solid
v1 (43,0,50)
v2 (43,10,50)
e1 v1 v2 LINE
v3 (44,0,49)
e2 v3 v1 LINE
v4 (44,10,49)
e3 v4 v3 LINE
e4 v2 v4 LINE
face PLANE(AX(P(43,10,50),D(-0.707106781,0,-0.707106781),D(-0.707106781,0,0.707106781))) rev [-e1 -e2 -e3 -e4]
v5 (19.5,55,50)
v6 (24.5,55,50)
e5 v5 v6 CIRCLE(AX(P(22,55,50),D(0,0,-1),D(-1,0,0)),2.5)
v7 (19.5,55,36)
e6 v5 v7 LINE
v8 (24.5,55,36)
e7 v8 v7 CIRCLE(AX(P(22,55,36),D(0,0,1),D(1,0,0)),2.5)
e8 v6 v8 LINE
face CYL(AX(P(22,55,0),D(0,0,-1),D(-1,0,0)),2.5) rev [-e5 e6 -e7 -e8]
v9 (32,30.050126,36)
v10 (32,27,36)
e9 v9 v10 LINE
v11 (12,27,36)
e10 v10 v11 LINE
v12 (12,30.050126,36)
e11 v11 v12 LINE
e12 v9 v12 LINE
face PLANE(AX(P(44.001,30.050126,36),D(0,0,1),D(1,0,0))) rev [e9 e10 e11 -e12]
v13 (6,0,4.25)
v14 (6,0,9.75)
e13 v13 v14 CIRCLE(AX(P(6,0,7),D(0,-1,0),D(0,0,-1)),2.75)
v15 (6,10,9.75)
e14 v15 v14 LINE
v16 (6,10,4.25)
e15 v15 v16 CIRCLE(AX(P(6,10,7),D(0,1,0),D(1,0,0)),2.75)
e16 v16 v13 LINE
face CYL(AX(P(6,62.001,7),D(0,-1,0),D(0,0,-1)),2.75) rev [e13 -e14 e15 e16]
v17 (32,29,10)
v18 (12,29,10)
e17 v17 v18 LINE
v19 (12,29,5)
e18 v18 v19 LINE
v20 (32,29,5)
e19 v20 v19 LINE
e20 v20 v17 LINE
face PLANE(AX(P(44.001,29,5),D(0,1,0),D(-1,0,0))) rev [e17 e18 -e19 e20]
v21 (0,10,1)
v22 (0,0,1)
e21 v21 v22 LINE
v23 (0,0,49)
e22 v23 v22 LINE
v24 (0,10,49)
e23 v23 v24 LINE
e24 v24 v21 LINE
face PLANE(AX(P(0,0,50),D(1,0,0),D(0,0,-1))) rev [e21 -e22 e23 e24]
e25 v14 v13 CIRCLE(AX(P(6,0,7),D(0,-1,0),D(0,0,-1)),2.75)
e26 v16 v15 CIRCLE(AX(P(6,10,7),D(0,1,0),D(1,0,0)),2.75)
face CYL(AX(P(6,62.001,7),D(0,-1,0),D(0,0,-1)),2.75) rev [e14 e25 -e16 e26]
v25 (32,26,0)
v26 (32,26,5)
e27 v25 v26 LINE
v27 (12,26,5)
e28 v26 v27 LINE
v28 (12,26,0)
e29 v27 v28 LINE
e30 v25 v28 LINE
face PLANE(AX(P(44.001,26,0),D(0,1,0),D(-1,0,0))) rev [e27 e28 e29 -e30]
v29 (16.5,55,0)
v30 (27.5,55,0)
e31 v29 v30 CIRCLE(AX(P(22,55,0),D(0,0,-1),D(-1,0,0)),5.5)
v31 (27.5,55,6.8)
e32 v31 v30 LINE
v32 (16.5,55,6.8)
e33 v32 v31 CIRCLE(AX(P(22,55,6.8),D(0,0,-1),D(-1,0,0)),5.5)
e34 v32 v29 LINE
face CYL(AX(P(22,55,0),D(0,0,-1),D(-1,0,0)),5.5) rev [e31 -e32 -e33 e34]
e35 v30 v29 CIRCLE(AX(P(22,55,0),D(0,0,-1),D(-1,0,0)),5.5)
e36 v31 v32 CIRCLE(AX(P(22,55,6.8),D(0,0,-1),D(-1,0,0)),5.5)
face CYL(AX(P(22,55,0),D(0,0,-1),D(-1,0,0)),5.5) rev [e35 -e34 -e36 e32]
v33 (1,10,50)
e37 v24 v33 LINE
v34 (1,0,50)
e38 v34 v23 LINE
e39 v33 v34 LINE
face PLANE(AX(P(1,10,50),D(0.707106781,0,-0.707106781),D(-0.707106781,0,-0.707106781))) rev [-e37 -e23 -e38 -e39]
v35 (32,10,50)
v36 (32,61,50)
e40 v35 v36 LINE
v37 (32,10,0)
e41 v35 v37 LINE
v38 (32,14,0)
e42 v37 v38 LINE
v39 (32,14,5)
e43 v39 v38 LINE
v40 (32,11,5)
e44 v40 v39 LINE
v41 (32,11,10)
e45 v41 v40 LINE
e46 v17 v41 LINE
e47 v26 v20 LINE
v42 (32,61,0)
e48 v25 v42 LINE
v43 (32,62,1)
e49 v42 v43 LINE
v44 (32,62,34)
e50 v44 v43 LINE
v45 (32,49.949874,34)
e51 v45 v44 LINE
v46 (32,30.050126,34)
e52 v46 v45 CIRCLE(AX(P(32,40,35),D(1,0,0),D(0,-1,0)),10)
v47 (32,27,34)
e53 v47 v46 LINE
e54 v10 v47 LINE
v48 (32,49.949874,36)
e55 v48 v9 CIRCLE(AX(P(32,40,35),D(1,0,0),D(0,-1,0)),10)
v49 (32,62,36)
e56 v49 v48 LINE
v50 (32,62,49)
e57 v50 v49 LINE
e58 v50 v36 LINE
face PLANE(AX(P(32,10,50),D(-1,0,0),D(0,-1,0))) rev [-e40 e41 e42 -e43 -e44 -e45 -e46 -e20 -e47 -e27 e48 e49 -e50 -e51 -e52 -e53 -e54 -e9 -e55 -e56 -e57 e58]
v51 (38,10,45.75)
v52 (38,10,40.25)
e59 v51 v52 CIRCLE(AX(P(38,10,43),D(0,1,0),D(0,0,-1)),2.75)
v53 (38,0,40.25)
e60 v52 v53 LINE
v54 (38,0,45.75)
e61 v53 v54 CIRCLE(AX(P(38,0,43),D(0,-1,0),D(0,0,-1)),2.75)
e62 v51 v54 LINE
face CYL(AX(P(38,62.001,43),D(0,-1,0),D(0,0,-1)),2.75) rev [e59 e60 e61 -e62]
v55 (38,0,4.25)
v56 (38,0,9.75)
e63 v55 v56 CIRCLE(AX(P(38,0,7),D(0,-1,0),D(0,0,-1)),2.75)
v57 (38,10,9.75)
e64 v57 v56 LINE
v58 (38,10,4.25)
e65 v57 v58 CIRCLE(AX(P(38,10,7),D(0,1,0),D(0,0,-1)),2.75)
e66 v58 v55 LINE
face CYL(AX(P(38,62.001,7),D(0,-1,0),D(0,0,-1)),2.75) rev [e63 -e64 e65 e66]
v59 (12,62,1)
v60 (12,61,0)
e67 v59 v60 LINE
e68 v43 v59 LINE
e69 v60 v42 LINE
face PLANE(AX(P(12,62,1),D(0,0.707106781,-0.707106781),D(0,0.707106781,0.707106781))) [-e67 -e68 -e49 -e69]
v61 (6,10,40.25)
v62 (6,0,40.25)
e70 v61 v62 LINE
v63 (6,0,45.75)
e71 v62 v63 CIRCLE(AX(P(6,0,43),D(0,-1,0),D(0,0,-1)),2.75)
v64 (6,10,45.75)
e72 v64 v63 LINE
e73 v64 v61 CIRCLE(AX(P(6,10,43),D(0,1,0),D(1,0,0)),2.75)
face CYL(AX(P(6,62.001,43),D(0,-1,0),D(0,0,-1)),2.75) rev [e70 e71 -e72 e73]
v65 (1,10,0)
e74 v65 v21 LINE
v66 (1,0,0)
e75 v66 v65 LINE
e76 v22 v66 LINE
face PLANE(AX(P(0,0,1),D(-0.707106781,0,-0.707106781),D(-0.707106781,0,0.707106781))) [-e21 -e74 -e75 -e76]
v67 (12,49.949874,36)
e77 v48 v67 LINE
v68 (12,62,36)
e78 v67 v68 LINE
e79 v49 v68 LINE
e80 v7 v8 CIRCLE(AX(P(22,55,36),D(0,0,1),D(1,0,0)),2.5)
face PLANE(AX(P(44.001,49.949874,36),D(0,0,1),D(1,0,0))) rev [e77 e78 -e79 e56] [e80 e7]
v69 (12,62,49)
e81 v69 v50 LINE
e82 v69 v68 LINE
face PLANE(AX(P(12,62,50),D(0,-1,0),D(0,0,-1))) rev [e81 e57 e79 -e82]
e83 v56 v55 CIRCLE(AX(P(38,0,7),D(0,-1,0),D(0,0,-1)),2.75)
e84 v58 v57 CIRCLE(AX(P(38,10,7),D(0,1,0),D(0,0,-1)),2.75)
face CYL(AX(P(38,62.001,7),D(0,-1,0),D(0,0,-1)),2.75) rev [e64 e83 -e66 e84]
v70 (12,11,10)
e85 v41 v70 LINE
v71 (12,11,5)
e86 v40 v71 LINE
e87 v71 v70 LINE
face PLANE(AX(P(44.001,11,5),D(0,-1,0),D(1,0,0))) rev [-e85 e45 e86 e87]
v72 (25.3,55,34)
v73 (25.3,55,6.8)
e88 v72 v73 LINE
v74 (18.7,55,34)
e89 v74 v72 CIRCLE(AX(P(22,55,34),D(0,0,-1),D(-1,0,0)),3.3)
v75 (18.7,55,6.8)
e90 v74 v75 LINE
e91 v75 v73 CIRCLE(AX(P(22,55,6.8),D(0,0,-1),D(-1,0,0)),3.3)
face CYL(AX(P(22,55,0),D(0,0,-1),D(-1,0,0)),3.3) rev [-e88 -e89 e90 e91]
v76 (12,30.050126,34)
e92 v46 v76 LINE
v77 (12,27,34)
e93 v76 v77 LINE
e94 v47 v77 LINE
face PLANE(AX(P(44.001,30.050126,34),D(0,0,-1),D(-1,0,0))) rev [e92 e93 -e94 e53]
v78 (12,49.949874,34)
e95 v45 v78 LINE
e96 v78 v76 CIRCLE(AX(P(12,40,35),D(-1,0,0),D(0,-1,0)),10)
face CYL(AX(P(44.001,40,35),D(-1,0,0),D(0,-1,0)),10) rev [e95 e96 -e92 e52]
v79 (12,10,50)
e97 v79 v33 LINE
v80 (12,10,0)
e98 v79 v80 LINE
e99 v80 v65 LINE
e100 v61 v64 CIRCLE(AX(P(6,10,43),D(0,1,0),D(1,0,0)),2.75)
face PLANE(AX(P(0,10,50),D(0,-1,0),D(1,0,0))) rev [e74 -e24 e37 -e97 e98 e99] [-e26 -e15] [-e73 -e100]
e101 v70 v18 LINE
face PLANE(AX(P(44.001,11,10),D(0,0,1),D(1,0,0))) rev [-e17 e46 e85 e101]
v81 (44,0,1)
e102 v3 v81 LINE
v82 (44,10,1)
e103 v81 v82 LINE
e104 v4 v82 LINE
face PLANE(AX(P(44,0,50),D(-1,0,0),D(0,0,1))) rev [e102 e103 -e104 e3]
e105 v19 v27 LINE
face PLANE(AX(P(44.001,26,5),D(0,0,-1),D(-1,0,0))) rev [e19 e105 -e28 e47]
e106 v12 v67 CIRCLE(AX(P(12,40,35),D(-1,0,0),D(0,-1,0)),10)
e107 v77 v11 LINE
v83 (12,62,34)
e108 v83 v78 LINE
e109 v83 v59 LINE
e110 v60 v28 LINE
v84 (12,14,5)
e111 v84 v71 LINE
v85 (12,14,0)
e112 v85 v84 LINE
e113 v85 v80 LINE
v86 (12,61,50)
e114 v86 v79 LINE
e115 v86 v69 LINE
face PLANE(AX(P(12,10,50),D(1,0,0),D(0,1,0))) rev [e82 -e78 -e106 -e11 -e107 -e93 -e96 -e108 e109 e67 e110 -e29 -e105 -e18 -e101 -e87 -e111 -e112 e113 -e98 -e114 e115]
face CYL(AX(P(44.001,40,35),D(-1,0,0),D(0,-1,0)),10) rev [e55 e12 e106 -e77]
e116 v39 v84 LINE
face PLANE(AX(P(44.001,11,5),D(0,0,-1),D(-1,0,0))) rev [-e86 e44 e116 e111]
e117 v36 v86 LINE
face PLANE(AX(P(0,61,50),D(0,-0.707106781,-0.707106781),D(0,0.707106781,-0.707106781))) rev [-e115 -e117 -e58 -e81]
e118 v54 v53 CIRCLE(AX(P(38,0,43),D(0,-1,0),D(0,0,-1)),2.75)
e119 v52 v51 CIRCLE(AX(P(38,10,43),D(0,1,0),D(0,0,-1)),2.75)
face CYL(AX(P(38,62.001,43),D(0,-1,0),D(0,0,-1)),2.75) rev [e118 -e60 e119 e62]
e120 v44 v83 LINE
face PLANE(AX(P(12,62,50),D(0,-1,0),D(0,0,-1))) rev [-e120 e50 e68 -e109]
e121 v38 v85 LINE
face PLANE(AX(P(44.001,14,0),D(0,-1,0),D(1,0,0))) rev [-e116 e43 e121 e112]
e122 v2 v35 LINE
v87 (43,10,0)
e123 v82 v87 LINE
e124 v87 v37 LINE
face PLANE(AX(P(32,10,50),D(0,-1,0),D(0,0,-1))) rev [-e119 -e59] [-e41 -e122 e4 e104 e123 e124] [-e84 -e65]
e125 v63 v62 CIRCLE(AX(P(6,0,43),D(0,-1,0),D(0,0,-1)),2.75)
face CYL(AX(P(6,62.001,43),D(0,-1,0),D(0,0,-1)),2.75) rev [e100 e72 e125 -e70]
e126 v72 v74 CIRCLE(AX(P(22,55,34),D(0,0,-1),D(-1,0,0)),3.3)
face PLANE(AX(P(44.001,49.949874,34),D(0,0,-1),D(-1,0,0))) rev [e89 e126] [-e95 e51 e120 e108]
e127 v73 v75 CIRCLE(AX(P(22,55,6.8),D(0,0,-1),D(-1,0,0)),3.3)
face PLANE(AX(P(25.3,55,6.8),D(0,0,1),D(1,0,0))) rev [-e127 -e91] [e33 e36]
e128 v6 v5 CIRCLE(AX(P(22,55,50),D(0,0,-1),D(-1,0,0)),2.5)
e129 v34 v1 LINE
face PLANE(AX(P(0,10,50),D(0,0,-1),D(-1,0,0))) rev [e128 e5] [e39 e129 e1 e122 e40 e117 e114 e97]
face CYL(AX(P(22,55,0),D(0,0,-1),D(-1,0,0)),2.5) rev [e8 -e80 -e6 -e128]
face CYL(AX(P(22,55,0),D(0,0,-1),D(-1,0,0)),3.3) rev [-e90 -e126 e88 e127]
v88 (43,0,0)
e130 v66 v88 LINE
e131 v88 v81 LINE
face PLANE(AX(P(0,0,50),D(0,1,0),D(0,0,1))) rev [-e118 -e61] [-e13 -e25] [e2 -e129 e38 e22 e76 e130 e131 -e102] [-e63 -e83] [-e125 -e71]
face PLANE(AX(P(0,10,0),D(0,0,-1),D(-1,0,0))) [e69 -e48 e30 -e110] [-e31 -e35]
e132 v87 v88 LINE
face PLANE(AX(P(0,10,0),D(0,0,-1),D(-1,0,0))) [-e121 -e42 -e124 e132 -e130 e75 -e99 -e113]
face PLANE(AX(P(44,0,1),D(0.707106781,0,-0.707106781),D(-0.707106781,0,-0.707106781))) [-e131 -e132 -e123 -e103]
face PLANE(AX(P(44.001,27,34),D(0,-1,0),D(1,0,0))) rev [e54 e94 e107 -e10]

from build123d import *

# Parameters (mm, degrees)
BOSS_EXTRUDE1_DEPTH                                  = 50
CUT_EXTRUDE1_REACH                                   = 92.995
SKETCH2_R                                            = 2.75
CUT_EXTRUDE2_REACH                                   = 87.837
HOLE_SIZE_PER_SOCKET_HEAD_CAP_SCREW_TYPE_D           = 6.6
HOLE_SIZE_PER_SOCKET_HEAD_CAP_SCREW_TYPE_DEPTH       = 34
HOLE_SIZE_PER_SOCKET_HEAD_CAP_SCREW_TYPE_CBORE_D     = 11
HOLE_SIZE_PER_SOCKET_HEAD_CAP_SCREW_TYPE_CBORE_DEPTH = 6.8
M6_TAPPED_HOLE1_D                                    = 5
CHAMFER1_SIZE                                        = 1


with BuildPart() as part:
    # Sketch1 → Boss-Extrude1 (new body)
    with BuildSketch(Plane.XY):
        Polygon((32, 10), (44, 10), (44, 0), (0, 0), (0, 10), (12, 10), (12, 62), (32, 62), align=None)
    extrude(amount=BOSS_EXTRUDE1_DEPTH)

    # Sketch2 → Cut-Extrude1 (cut, up to next)
    with BuildSketch(Plane.XZ, mode=Mode.PRIVATE) as cut_extrude1_sk1:
        with Locations(Location((6, 43, 0), (0, 0, 270))):
            Circle(SKETCH2_R)
    cut_extrude1_tool1 = extrude(cut_extrude1_sk1.sketch, amount=-CUT_EXTRUDE1_REACH, mode=Mode.PRIVATE) & part.part
    # Sketch2 → Cut-Extrude1 (cut, up to next)
    with BuildSketch(Plane.XZ, mode=Mode.PRIVATE) as cut_extrude1_sk2:
        with Locations(Location((6, 7, 0), (0, 0, 270))):
            Circle(SKETCH2_R)
    cut_extrude1_tool2 = extrude(cut_extrude1_sk2.sketch, amount=-CUT_EXTRUDE1_REACH, mode=Mode.PRIVATE) & part.part
    # Sketch2 → Cut-Extrude1 (cut, up to next)
    with BuildSketch(Plane.XZ, mode=Mode.PRIVATE) as cut_extrude1_sk3:
        with Locations(Location((38, 43, 0), (0, 0, 270))):
            Circle(SKETCH2_R)
    cut_extrude1_tool3 = extrude(cut_extrude1_sk3.sketch, amount=-CUT_EXTRUDE1_REACH, mode=Mode.PRIVATE) & part.part
    # Sketch2 → Cut-Extrude1 (cut, up to next)
    with BuildSketch(Plane.XZ, mode=Mode.PRIVATE) as cut_extrude1_sk4:
        with Locations(Location((38, 7, 0), (0, 0, 270))):
            Circle(SKETCH2_R)
    cut_extrude1_tool4 = extrude(cut_extrude1_sk4.sketch, amount=-CUT_EXTRUDE1_REACH, mode=Mode.PRIVATE) & part.part
    add(cut_extrude1_tool1.solids().sort_by_distance((6, 0, 43))[0], mode=Mode.SUBTRACT)
    add(cut_extrude1_tool2.solids().sort_by_distance((6, 0, 7))[0], mode=Mode.SUBTRACT)
    add(cut_extrude1_tool3.solids().sort_by_distance((38, 0, 43))[0], mode=Mode.SUBTRACT)
    add(cut_extrude1_tool4.solids().sort_by_distance((38, 0, 7))[0], mode=Mode.SUBTRACT)

    # Sketch3 → Cut-Extrude2 (cut, up to next)
    with BuildSketch(Plane.ZY.offset(-12), mode=Mode.PRIVATE) as cut_extrude2_sk1:
        with BuildLine():
            Line((34, 49.949874371), (34, 62))
            Line((34, 62), (36, 62))
            Line((36, 62), (36, 49.949874371))
            ThreePointArc((36, 49.949874371), (45, 40), (36, 30.050125629))
            Line((36, 30.050125629), (36, 27))
            Line((36, 27), (34, 27))
            Line((34, 27), (34, 30.050125629))
            ThreePointArc((34, 30.050125629), (25, 40), (34, 49.949874371))
        make_face()
    cut_extrude2_tool1 = extrude(cut_extrude2_sk1.sketch, amount=-CUT_EXTRUDE2_REACH, mode=Mode.PRIVATE) & part.part
    # Sketch3 → Cut-Extrude2 (cut, up to next)
    with BuildSketch(Plane.ZY.offset(-12), mode=Mode.PRIVATE) as cut_extrude2_sk2:
        Polygon((5, 26), (5, 29), (10, 29), (10, 11), (5, 11), (5, 14), (0, 14), (0, 26), align=None)
    cut_extrude2_tool2 = extrude(cut_extrude2_sk2.sketch, amount=-CUT_EXTRUDE2_REACH, mode=Mode.PRIVATE) & part.part
    add(cut_extrude2_tool1.solids().sort_by_distance((12, 40.915096, 35))[0], mode=Mode.SUBTRACT)
    add(cut_extrude2_tool2.solids().sort_by_distance((12, 20, 5.5))[0], mode=Mode.SUBTRACT)

    # Hole size per socket head cap screw type 1
    with Locations(Plane(origin=(0, 0, 0), x_dir=(-1, 0, 0), z_dir=(0, 0, -1))):
        with Locations((-22, 55)):
            CounterBoreHole(HOLE_SIZE_PER_SOCKET_HEAD_CAP_SCREW_TYPE_D / 2, HOLE_SIZE_PER_SOCKET_HEAD_CAP_SCREW_TYPE_CBORE_D / 2, HOLE_SIZE_PER_SOCKET_HEAD_CAP_SCREW_TYPE_CBORE_DEPTH, depth=HOLE_SIZE_PER_SOCKET_HEAD_CAP_SCREW_TYPE_DEPTH)

    # M6 Tapped Hole1 (through all)
    with Locations(Plane(origin=(0, 0, 0), x_dir=(-1, 0, 0), z_dir=(0, 0, -1))):
        with Locations((-22, 55)):
            Hole(M6_TAPPED_HOLE1_D / 2)

    # Chamfer1
    chamfer1_edges = [part.edges().sort_by_distance(p)[0] for p in [
        (44, 5, 50),
        (0, 5, 0),
        (22, 62, 50),
        (0, 5, 50),
        (22, 62, 0),
        (44, 5, 0),
    ]]
    chamfer(chamfer1_edges, length=CHAMFER1_SIZE)


solid = part.part
